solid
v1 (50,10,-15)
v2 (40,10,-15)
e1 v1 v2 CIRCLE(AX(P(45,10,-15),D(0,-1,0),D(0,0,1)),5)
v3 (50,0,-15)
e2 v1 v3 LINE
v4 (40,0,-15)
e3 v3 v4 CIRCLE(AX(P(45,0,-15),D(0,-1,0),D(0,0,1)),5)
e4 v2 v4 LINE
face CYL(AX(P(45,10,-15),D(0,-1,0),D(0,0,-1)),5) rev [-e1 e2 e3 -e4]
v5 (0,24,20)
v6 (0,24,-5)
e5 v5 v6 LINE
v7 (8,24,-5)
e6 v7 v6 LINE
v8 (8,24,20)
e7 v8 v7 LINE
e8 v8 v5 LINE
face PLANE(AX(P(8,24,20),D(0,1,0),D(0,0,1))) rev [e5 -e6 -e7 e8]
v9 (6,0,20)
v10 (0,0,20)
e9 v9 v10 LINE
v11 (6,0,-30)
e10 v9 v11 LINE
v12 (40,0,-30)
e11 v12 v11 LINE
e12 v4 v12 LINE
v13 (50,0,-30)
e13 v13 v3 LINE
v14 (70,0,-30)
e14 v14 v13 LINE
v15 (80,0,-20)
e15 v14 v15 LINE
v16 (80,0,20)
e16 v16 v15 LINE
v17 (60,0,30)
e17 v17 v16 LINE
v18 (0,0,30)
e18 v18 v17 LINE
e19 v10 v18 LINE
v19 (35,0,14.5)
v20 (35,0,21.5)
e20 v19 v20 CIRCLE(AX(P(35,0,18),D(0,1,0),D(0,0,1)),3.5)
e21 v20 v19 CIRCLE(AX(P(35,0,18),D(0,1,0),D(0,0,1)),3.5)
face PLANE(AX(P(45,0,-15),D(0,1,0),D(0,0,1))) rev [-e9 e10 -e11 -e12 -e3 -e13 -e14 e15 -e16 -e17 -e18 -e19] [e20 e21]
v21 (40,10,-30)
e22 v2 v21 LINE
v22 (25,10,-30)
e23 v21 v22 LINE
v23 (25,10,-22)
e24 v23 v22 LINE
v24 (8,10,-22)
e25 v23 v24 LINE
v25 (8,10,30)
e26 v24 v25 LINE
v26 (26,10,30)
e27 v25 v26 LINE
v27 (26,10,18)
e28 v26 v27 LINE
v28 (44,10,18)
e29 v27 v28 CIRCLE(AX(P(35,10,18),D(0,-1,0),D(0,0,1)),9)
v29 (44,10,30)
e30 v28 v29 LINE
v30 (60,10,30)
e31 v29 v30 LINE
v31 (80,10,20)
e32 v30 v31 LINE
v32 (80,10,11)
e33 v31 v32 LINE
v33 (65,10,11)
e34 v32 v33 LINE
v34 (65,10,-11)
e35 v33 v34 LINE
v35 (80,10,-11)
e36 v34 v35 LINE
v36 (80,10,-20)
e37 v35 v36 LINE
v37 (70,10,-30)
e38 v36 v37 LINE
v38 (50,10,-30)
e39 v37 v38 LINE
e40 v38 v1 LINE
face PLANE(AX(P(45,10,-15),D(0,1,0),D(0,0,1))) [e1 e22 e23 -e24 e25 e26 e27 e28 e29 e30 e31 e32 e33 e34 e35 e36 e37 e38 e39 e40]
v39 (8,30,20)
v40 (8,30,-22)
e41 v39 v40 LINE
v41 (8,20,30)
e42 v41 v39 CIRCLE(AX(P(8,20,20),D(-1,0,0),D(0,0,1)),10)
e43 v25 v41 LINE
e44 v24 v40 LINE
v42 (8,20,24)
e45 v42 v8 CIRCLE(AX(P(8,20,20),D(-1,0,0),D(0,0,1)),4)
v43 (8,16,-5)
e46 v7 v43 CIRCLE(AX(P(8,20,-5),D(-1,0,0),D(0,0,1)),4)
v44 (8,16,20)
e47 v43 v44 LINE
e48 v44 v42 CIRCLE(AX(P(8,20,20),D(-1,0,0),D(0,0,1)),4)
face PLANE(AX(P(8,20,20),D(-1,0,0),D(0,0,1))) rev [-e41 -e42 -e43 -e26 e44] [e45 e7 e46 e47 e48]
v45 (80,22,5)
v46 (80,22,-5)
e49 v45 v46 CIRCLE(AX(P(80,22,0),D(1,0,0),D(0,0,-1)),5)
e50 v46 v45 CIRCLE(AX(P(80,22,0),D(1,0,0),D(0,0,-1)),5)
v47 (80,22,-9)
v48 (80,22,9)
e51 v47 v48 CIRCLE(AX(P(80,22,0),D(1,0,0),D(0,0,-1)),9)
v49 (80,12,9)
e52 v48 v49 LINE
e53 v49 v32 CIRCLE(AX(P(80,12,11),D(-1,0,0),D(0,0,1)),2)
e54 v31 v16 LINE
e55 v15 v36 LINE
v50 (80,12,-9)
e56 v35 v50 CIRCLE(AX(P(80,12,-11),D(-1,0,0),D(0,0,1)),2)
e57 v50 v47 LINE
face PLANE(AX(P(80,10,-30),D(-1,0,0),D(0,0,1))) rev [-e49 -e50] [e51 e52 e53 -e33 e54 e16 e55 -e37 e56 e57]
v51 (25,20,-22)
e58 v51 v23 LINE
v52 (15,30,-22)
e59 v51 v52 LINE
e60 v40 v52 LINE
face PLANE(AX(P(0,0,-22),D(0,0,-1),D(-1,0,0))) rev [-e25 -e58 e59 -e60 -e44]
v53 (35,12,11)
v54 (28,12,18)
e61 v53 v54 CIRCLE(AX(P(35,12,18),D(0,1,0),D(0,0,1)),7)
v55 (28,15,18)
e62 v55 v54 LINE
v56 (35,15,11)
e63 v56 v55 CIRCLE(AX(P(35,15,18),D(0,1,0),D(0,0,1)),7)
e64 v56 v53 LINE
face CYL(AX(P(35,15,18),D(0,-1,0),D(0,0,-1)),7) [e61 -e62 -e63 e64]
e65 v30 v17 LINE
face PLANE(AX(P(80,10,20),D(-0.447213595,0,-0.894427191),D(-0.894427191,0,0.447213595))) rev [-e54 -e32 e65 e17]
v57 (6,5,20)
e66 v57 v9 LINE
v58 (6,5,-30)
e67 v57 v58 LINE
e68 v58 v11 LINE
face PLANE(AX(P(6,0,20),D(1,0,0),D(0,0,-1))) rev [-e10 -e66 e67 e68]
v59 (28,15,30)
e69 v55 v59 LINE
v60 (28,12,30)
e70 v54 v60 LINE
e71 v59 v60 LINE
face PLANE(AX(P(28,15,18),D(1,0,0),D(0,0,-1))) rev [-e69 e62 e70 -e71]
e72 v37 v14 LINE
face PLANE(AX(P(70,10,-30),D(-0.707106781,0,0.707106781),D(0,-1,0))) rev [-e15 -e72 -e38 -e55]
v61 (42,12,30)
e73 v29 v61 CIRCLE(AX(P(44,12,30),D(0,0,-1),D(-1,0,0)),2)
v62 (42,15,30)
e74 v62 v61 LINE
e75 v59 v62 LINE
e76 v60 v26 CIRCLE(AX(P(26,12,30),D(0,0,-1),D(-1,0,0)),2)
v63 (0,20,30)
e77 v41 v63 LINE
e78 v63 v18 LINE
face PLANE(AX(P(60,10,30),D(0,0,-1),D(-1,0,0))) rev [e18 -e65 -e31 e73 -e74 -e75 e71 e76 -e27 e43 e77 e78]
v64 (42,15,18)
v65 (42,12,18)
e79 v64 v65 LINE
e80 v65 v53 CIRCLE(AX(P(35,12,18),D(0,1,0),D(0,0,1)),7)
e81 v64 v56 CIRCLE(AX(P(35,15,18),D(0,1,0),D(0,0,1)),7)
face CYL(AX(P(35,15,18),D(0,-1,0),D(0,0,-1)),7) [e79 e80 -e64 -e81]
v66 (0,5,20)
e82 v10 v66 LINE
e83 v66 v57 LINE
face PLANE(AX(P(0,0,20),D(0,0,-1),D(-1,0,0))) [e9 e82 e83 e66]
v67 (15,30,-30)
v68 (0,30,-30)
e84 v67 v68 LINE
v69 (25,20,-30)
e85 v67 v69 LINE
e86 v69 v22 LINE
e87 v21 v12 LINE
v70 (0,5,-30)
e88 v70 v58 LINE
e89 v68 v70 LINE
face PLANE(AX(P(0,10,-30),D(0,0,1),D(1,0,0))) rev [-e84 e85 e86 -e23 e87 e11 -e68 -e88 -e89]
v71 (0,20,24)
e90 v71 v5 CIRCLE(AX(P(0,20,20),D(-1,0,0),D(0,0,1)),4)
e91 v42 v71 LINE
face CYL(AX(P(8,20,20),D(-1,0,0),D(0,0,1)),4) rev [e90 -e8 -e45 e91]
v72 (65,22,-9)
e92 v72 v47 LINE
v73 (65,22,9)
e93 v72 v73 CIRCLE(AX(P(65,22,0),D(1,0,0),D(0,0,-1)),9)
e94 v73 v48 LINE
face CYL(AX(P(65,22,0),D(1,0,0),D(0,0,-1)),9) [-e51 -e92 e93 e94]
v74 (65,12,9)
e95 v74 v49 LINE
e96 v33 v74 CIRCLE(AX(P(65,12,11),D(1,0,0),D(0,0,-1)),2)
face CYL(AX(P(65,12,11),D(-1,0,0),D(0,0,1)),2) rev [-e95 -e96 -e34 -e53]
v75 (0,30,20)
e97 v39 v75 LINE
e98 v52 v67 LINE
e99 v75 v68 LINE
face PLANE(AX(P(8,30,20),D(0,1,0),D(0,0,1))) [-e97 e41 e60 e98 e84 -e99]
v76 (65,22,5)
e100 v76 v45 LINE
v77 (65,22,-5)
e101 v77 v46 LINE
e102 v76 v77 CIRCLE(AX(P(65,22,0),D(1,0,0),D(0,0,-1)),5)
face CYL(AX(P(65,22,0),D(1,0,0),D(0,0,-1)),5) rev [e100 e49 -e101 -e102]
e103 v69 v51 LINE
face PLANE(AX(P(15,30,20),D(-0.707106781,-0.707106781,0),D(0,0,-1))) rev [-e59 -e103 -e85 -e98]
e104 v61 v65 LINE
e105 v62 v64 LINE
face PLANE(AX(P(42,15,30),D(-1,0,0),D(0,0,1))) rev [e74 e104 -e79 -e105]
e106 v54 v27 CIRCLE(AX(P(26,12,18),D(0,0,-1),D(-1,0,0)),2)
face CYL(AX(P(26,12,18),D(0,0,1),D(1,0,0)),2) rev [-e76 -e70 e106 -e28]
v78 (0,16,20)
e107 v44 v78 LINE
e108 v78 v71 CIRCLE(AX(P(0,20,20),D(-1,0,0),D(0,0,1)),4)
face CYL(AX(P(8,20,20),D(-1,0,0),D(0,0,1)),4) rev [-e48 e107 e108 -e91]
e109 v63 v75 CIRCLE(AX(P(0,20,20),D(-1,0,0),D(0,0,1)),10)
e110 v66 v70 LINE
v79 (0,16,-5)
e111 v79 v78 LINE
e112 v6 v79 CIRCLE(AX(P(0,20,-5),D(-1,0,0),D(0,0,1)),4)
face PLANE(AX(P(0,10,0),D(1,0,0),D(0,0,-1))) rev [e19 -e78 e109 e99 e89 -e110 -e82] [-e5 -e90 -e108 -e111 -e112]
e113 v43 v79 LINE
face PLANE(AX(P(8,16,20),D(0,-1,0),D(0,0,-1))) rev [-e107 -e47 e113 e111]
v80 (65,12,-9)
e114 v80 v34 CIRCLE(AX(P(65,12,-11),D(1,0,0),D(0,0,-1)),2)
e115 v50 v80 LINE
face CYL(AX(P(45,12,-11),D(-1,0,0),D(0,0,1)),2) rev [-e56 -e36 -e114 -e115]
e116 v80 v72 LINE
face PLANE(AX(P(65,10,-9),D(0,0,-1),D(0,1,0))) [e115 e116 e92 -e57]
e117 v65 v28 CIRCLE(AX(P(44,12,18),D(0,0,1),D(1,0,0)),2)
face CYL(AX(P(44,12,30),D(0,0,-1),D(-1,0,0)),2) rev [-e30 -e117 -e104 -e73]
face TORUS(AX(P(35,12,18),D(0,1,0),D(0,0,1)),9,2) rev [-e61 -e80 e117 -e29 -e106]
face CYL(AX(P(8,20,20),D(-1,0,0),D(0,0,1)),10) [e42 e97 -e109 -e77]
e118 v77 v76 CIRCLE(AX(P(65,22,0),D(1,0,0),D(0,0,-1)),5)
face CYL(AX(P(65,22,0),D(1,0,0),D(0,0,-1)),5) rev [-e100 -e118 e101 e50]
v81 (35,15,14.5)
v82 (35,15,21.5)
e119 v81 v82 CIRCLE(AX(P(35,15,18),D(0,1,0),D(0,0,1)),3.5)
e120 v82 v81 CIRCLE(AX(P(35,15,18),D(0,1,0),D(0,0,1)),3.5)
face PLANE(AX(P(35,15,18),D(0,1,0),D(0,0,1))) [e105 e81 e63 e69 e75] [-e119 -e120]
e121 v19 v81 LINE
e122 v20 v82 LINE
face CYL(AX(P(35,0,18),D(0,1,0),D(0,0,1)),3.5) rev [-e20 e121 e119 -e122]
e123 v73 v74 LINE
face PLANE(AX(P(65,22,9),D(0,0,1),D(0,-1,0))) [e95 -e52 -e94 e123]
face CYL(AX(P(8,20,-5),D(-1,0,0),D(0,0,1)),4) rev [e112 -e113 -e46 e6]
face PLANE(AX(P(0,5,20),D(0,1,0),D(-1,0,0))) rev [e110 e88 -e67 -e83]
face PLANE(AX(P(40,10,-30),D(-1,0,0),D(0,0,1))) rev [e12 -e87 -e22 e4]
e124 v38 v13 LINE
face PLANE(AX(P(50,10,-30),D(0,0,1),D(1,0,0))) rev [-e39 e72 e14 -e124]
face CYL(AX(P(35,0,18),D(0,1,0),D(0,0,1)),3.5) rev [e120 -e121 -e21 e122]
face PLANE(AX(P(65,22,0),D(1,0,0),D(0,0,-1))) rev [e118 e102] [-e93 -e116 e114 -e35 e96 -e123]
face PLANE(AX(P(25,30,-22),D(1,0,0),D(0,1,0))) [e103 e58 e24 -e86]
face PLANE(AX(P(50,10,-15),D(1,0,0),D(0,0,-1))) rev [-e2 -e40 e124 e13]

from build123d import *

# Parameters (mm, degrees)
BASE_PLATE_80X60X10_DEPTH      = 10
BASE_CORNER_CHAMFER_10_SIZE    = 10
SLOTTED_UPRIGHT_WALL_DEPTH     = 8
SIDE_BLOCK_SKETCH_W            = 17
SIDE_BLOCK_SKETCH_H            = 20
SIDE_BLOCK_25_DEPTH            = 8
SIDE_BLOCK_TOP_CHAMFER_10_SIZE = 10
HOLE_PAD_DEPTH                 = 5
PAD_HOLE_SKETCH_R              = 3.5
PAD_HOLE_7_DEPTH               = 87.746757864
PIVOT_LUG_SKETCH_R             = 5
PIVOT_LUG_DEPTH                = 15
LUG_ROOT_FILLET_R2_R           = 2
RELIEF_GROOVE_SKETCH_W         = 6
RELIEF_GROOVE_SKETCH_H         = 5
RELIEF_GROOVE_6X5_DEPTH        = 50


with BuildPart() as part:
    # Base Plate Sketch → Base Plate 80x60x10 (new body)
    with BuildSketch(Plane(origin=(0, 0, 0), x_dir=(1, 0, 0), z_dir=(0, 1, 0))):
        with BuildLine():
            Line((0, 0), (0, 30))
            Line((0, 30), (40, 30))
            Line((40, 30), (40, 15))
            ThreePointArc((40, 15), (45, 10), (50, 15))
            Line((50, 15), (50, 30))
            Line((50, 30), (80, 30))
            Line((80, 30), (80, -20))
            Line((80, -20), (60, -30))
            Line((60, -30), (0, -30))
            Line((0, -30), (0, 0))
        make_face()
    extrude(amount=BASE_PLATE_80X60X10_DEPTH)

    # Base Corner Chamfer 10
    base_corner_chamfer_10_edges = [part.edges().sort_by_distance(p)[0] for p in [
        (80, 5, -30),
    ]]
    chamfer(base_corner_chamfer_10_edges, length=BASE_CORNER_CHAMFER_10_SIZE)

    # Slotted Wall Sketch → Slotted Upright Wall (add)
    with BuildSketch(Plane.ZY):
        with BuildLine():
            Line((20, 30), (-30, 30))
            Line((-30, 30), (-30, 10))
            Line((-30, 10), (30, 10))
            Line((30, 10), (30, 20))
            ThreePointArc((30, 20), (27.071067812, 27.071067812), (20, 30))
        make_face()
        with BuildLine():
            Line((20, 16), (-5, 16))
            ThreePointArc((-5, 16), (-9, 20), (-5, 24))
            Line((-5, 24), (20, 24))
            ThreePointArc((20, 24), (24, 20), (20, 16))
        make_face(mode=Mode.SUBTRACT)
    extrude(amount=-SLOTTED_UPRIGHT_WALL_DEPTH)

    # Side Block Sketch → Side Block 25 (add)
    with BuildSketch(Plane(origin=(0, 0, -30), x_dir=(-1, 0, 0), z_dir=(0, 0, -1))):
        with Locations((-16.5, 20)):
            Rectangle(SIDE_BLOCK_SKETCH_W, SIDE_BLOCK_SKETCH_H)
    extrude(amount=-SIDE_BLOCK_25_DEPTH)

    # Side Block Top Chamfer 10
    side_block_top_chamfer_10_edges = [part.edges().sort_by_distance(p)[0] for p in [
        (25, 30, -26),
    ]]
    chamfer(side_block_top_chamfer_10_edges, length=SIDE_BLOCK_TOP_CHAMFER_10_SIZE)

    # Hole Pad Sketch → Hole Pad (add)
    with BuildSketch(Plane(origin=(0, 10, 0), x_dir=(1, 0, 0), z_dir=(0, 1, 0))):
        with BuildLine():
            Line((28, -18), (28, -30))
            Line((28, -30), (42, -30))
            Line((42, -30), (42, -18))
            ThreePointArc((42, -18), (35, -11), (28, -18))
        make_face()
    extrude(amount=HOLE_PAD_DEPTH)

    # Pad Hole Sketch → Pad Hole Ø7 (cut, through all)
    with BuildSketch(Plane(origin=(0, 15, 0), x_dir=(1, 0, 0), z_dir=(0, 1, 0))):
        with Locations(Location((35, -18, 0), (0, 0, 270))):
            Circle(PAD_HOLE_SKETCH_R)
    extrude(amount=-PAD_HOLE_7_DEPTH, mode=Mode.SUBTRACT)

    # Pivot Lug Sketch → Pivot Lug (add)
    with BuildSketch(Plane(origin=(80, 0, 0), x_dir=(0, 0, -1), z_dir=(1, 0, 0))):
        with BuildLine():
            Line((-9, 22), (-9, 10))
            Line((-9, 10), (9, 10))
            Line((9, 10), (9, 22))
            ThreePointArc((9, 22), (0, 31), (-9, 22))
        make_face()
        with Locations((0, 22)):
            Circle(PIVOT_LUG_SKETCH_R, mode=Mode.SUBTRACT)
    extrude(amount=-PIVOT_LUG_DEPTH)

    # Lug Root Fillet R2
    lug_root_fillet_r2_edges = [part.edges().sort_by_distance(p)[0] for p in [
        (72.5, 10, -9),
        (72.5, 10, 9),
        (35, 10, 11),
        (28, 10, 24),
        (42, 10, 24),
    ]]
    fillet(lug_root_fillet_r2_edges, radius=LUG_ROOT_FILLET_R2_R)

    # Relief Groove Sketch → Relief Groove 6x5 (cut)
    with BuildSketch(Plane(origin=(0, 0, -30), x_dir=(-1, 0, 0), z_dir=(0, 0, -1))):
        with Locations((-3, 2.5)):
            Rectangle(RELIEF_GROOVE_SKETCH_W, RELIEF_GROOVE_SKETCH_H)
    extrude(amount=-RELIEF_GROOVE_6X5_DEPTH, mode=Mode.SUBTRACT)


solid = part.part
